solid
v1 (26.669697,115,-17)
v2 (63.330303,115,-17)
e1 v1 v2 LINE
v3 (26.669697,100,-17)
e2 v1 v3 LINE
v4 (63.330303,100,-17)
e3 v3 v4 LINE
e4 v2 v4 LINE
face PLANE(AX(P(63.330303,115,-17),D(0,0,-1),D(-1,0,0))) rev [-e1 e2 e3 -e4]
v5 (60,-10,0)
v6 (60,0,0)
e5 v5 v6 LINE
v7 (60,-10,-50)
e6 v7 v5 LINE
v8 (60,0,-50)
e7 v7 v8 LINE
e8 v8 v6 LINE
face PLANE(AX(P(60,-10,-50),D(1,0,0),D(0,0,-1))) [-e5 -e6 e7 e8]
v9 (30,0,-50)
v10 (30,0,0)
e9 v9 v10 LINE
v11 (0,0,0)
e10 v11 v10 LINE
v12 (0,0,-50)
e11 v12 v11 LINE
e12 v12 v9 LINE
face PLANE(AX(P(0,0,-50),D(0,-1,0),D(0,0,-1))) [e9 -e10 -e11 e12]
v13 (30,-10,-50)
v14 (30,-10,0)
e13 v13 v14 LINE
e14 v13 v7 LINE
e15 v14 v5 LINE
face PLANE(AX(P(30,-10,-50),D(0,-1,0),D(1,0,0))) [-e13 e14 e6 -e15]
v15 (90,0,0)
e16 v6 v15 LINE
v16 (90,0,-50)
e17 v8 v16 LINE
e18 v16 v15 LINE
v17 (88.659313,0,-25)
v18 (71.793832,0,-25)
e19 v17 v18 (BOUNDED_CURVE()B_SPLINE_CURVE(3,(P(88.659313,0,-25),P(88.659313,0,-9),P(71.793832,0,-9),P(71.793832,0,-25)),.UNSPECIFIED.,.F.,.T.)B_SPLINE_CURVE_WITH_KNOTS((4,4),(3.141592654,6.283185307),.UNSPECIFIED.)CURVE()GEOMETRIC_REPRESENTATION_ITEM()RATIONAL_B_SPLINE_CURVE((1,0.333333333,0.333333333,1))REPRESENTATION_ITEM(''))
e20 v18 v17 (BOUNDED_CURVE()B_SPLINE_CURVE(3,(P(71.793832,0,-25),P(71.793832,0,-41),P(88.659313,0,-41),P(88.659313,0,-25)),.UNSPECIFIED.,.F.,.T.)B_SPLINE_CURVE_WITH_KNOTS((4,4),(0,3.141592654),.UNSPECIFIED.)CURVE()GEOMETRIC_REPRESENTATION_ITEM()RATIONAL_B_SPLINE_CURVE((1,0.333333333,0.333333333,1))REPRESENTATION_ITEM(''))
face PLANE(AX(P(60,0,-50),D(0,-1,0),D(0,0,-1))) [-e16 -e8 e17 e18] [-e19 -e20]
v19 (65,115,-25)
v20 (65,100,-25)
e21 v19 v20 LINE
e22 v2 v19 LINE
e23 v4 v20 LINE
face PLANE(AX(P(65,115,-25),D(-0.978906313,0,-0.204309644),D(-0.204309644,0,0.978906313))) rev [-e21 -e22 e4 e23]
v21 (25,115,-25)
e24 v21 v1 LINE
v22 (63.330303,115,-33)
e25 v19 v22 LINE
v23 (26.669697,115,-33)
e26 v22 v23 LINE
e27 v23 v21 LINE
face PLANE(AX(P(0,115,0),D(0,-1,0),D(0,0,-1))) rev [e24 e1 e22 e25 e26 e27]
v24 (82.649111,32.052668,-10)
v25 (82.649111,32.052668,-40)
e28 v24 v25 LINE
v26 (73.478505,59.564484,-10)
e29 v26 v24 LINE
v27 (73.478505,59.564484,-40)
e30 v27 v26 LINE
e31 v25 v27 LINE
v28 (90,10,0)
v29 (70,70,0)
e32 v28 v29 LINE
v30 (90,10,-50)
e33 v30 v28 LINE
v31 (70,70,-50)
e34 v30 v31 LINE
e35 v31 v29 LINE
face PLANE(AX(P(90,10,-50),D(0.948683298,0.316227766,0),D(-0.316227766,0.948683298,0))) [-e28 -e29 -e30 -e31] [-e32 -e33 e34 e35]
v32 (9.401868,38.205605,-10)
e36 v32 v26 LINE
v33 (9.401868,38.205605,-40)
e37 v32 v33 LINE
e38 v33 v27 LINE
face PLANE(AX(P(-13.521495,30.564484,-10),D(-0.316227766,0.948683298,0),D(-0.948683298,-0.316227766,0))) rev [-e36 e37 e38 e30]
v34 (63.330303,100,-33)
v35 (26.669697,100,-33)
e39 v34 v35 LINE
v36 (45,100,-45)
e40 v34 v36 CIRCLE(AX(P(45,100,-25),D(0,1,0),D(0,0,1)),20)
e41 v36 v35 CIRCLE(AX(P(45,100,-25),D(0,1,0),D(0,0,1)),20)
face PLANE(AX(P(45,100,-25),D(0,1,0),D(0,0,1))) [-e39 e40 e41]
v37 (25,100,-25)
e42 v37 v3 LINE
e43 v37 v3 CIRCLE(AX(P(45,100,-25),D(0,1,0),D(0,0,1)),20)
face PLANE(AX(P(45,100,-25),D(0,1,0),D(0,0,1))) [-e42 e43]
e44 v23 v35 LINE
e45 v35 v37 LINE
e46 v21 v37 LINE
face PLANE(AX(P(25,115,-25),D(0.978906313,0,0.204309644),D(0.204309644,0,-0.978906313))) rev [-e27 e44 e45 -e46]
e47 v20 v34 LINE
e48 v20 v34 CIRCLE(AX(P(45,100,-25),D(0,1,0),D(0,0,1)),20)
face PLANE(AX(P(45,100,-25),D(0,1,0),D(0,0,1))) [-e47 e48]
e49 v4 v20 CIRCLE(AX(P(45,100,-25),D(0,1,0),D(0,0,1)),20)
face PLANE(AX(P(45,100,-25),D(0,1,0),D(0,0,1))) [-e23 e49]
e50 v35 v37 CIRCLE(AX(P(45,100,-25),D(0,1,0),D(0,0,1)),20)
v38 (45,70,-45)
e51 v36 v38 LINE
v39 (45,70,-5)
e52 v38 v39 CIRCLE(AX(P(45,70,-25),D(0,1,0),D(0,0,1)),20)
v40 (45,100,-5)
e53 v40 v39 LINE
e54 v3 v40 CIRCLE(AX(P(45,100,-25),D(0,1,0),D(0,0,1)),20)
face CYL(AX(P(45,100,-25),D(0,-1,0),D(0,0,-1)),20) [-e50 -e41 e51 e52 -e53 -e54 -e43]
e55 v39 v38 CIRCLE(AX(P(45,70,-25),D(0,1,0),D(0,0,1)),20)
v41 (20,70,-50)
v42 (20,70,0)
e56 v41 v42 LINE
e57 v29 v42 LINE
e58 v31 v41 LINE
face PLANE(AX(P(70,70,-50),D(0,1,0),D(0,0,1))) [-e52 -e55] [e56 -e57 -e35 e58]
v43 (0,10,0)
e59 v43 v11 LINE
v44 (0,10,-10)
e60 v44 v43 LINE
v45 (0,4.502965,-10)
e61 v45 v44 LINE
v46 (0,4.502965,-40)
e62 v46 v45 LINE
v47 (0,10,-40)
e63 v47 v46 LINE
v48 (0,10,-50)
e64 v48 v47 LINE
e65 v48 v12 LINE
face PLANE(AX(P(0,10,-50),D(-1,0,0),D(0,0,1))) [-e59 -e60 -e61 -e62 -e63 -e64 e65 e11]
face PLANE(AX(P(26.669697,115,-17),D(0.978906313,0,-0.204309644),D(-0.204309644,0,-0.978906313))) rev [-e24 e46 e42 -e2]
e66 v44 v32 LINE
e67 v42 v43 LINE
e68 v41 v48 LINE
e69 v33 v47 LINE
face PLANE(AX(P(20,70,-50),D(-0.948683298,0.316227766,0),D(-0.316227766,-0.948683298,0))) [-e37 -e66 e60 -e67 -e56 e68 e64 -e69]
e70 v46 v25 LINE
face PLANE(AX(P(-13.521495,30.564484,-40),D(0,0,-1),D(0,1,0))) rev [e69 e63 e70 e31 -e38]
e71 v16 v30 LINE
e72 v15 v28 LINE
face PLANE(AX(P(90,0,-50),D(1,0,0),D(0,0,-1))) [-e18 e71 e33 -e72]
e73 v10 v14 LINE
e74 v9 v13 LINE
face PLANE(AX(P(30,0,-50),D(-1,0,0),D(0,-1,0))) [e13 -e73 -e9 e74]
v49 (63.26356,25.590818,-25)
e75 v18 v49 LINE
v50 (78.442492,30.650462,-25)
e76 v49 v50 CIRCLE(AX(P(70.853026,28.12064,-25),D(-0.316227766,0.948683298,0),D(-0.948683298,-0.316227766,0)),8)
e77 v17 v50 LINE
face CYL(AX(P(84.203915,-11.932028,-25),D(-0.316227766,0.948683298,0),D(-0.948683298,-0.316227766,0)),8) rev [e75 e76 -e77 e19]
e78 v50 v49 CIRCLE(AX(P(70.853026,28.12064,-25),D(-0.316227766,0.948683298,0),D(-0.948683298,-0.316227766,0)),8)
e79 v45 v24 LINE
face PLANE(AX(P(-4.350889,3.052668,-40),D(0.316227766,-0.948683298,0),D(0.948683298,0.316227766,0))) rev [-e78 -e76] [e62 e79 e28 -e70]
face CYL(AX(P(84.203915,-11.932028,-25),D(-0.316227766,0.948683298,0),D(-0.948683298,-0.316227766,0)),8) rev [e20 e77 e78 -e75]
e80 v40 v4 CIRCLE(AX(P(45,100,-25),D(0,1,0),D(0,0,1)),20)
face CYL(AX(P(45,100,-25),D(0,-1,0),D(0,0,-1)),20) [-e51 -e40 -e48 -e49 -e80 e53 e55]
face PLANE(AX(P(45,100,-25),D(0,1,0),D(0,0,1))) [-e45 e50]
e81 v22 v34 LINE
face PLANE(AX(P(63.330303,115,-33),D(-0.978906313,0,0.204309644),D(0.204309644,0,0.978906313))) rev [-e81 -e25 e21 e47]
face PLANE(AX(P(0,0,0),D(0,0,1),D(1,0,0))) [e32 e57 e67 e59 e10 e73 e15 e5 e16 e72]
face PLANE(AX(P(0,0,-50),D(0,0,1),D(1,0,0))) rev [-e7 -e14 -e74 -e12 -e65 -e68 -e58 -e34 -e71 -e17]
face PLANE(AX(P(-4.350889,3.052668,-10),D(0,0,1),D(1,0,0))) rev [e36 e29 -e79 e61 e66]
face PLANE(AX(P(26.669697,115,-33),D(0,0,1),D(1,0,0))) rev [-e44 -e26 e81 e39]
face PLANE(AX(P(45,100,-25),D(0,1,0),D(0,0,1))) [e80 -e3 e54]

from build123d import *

# Parameters (mm, degrees)
BASE_BODY_DEPTH              = 50
SIDE_WINDOW_SKETCH_W         = 30
SIDE_WINDOW_SKETCH_H         = 29
SIDE_WINDOW_CUT_DEPTH        = 107.395488626
CYLINDRICAL_BOSS_40_SKETCH_R = 20
CYLINDRICAL_BOSS_40_DEPTH    = 30
TOP_KEY_DEPTH                = 15
HOLE_16_SKETCH_R             = 8
HOLE_16_DEPTH                = 153.165355608


with BuildPart() as part:
    # Base Body Profile Sketch → Base Body (new body)
    with BuildSketch(Plane.XY):
        Polygon((0, 0), (30, 0), (30, -10), (60, -10), (60, 0), (90, 0), (90, 10), (70, 70), (20, 70), (0, 10), align=None)
    extrude(amount=-BASE_BODY_DEPTH)

    # Side Window Sketch → Side Window Cut (cut, through all)
    with BuildSketch(Plane(origin=(84, 28, 0), x_dir=(0, 0, -1), z_dir=(0.948683298050514, 0.31622776601683783, 0))):
        with Locations((25, 18.771887242)):
            Rectangle(SIDE_WINDOW_SKETCH_W, SIDE_WINDOW_SKETCH_H)
    extrude(amount=-SIDE_WINDOW_CUT_DEPTH, mode=Mode.SUBTRACT)

    # Cylindrical Boss Ø40 Sketch → Cylindrical Boss Ø40 (add)
    with BuildSketch(Plane(origin=(0, 70, 0), x_dir=(1, 0, 0), z_dir=(0, 1, 0))):
        with Locations(Location((45, 25, 0), (0, 0, 270))):
            Circle(CYLINDRICAL_BOSS_40_SKETCH_R)
    extrude(amount=CYLINDRICAL_BOSS_40_DEPTH)

    # Top Key Sketch → Top Key (add)
    with BuildSketch(Plane(origin=(0, 100, 0), x_dir=(1, 0, 0), z_dir=(0, 1, 0))):
        Polygon((25, 25), (26.66969722, 33), (63.33030278, 33), (65, 25), (63.33030278, 17), (26.66969722, 17), align=None)
    extrude(amount=TOP_KEY_DEPTH)

    # Hole Ø16 Sketch → Hole Ø16 (cut, through all)
    with BuildSketch(Plane(origin=(-1.350889359, 4.052668078, 0), x_dir=(0.9486832980505139, 0.31622776601683794, 0), z_dir=(-0.31622776601683794, 0.9486832980505139, 0))):
        with Locations(Location((76.109609582, 25, 0), (0, 0, 180))):
            Circle(HOLE_16_SKETCH_R)
    extrude(amount=-HOLE_16_DEPTH, mode=Mode.SUBTRACT)


solid = part.part
